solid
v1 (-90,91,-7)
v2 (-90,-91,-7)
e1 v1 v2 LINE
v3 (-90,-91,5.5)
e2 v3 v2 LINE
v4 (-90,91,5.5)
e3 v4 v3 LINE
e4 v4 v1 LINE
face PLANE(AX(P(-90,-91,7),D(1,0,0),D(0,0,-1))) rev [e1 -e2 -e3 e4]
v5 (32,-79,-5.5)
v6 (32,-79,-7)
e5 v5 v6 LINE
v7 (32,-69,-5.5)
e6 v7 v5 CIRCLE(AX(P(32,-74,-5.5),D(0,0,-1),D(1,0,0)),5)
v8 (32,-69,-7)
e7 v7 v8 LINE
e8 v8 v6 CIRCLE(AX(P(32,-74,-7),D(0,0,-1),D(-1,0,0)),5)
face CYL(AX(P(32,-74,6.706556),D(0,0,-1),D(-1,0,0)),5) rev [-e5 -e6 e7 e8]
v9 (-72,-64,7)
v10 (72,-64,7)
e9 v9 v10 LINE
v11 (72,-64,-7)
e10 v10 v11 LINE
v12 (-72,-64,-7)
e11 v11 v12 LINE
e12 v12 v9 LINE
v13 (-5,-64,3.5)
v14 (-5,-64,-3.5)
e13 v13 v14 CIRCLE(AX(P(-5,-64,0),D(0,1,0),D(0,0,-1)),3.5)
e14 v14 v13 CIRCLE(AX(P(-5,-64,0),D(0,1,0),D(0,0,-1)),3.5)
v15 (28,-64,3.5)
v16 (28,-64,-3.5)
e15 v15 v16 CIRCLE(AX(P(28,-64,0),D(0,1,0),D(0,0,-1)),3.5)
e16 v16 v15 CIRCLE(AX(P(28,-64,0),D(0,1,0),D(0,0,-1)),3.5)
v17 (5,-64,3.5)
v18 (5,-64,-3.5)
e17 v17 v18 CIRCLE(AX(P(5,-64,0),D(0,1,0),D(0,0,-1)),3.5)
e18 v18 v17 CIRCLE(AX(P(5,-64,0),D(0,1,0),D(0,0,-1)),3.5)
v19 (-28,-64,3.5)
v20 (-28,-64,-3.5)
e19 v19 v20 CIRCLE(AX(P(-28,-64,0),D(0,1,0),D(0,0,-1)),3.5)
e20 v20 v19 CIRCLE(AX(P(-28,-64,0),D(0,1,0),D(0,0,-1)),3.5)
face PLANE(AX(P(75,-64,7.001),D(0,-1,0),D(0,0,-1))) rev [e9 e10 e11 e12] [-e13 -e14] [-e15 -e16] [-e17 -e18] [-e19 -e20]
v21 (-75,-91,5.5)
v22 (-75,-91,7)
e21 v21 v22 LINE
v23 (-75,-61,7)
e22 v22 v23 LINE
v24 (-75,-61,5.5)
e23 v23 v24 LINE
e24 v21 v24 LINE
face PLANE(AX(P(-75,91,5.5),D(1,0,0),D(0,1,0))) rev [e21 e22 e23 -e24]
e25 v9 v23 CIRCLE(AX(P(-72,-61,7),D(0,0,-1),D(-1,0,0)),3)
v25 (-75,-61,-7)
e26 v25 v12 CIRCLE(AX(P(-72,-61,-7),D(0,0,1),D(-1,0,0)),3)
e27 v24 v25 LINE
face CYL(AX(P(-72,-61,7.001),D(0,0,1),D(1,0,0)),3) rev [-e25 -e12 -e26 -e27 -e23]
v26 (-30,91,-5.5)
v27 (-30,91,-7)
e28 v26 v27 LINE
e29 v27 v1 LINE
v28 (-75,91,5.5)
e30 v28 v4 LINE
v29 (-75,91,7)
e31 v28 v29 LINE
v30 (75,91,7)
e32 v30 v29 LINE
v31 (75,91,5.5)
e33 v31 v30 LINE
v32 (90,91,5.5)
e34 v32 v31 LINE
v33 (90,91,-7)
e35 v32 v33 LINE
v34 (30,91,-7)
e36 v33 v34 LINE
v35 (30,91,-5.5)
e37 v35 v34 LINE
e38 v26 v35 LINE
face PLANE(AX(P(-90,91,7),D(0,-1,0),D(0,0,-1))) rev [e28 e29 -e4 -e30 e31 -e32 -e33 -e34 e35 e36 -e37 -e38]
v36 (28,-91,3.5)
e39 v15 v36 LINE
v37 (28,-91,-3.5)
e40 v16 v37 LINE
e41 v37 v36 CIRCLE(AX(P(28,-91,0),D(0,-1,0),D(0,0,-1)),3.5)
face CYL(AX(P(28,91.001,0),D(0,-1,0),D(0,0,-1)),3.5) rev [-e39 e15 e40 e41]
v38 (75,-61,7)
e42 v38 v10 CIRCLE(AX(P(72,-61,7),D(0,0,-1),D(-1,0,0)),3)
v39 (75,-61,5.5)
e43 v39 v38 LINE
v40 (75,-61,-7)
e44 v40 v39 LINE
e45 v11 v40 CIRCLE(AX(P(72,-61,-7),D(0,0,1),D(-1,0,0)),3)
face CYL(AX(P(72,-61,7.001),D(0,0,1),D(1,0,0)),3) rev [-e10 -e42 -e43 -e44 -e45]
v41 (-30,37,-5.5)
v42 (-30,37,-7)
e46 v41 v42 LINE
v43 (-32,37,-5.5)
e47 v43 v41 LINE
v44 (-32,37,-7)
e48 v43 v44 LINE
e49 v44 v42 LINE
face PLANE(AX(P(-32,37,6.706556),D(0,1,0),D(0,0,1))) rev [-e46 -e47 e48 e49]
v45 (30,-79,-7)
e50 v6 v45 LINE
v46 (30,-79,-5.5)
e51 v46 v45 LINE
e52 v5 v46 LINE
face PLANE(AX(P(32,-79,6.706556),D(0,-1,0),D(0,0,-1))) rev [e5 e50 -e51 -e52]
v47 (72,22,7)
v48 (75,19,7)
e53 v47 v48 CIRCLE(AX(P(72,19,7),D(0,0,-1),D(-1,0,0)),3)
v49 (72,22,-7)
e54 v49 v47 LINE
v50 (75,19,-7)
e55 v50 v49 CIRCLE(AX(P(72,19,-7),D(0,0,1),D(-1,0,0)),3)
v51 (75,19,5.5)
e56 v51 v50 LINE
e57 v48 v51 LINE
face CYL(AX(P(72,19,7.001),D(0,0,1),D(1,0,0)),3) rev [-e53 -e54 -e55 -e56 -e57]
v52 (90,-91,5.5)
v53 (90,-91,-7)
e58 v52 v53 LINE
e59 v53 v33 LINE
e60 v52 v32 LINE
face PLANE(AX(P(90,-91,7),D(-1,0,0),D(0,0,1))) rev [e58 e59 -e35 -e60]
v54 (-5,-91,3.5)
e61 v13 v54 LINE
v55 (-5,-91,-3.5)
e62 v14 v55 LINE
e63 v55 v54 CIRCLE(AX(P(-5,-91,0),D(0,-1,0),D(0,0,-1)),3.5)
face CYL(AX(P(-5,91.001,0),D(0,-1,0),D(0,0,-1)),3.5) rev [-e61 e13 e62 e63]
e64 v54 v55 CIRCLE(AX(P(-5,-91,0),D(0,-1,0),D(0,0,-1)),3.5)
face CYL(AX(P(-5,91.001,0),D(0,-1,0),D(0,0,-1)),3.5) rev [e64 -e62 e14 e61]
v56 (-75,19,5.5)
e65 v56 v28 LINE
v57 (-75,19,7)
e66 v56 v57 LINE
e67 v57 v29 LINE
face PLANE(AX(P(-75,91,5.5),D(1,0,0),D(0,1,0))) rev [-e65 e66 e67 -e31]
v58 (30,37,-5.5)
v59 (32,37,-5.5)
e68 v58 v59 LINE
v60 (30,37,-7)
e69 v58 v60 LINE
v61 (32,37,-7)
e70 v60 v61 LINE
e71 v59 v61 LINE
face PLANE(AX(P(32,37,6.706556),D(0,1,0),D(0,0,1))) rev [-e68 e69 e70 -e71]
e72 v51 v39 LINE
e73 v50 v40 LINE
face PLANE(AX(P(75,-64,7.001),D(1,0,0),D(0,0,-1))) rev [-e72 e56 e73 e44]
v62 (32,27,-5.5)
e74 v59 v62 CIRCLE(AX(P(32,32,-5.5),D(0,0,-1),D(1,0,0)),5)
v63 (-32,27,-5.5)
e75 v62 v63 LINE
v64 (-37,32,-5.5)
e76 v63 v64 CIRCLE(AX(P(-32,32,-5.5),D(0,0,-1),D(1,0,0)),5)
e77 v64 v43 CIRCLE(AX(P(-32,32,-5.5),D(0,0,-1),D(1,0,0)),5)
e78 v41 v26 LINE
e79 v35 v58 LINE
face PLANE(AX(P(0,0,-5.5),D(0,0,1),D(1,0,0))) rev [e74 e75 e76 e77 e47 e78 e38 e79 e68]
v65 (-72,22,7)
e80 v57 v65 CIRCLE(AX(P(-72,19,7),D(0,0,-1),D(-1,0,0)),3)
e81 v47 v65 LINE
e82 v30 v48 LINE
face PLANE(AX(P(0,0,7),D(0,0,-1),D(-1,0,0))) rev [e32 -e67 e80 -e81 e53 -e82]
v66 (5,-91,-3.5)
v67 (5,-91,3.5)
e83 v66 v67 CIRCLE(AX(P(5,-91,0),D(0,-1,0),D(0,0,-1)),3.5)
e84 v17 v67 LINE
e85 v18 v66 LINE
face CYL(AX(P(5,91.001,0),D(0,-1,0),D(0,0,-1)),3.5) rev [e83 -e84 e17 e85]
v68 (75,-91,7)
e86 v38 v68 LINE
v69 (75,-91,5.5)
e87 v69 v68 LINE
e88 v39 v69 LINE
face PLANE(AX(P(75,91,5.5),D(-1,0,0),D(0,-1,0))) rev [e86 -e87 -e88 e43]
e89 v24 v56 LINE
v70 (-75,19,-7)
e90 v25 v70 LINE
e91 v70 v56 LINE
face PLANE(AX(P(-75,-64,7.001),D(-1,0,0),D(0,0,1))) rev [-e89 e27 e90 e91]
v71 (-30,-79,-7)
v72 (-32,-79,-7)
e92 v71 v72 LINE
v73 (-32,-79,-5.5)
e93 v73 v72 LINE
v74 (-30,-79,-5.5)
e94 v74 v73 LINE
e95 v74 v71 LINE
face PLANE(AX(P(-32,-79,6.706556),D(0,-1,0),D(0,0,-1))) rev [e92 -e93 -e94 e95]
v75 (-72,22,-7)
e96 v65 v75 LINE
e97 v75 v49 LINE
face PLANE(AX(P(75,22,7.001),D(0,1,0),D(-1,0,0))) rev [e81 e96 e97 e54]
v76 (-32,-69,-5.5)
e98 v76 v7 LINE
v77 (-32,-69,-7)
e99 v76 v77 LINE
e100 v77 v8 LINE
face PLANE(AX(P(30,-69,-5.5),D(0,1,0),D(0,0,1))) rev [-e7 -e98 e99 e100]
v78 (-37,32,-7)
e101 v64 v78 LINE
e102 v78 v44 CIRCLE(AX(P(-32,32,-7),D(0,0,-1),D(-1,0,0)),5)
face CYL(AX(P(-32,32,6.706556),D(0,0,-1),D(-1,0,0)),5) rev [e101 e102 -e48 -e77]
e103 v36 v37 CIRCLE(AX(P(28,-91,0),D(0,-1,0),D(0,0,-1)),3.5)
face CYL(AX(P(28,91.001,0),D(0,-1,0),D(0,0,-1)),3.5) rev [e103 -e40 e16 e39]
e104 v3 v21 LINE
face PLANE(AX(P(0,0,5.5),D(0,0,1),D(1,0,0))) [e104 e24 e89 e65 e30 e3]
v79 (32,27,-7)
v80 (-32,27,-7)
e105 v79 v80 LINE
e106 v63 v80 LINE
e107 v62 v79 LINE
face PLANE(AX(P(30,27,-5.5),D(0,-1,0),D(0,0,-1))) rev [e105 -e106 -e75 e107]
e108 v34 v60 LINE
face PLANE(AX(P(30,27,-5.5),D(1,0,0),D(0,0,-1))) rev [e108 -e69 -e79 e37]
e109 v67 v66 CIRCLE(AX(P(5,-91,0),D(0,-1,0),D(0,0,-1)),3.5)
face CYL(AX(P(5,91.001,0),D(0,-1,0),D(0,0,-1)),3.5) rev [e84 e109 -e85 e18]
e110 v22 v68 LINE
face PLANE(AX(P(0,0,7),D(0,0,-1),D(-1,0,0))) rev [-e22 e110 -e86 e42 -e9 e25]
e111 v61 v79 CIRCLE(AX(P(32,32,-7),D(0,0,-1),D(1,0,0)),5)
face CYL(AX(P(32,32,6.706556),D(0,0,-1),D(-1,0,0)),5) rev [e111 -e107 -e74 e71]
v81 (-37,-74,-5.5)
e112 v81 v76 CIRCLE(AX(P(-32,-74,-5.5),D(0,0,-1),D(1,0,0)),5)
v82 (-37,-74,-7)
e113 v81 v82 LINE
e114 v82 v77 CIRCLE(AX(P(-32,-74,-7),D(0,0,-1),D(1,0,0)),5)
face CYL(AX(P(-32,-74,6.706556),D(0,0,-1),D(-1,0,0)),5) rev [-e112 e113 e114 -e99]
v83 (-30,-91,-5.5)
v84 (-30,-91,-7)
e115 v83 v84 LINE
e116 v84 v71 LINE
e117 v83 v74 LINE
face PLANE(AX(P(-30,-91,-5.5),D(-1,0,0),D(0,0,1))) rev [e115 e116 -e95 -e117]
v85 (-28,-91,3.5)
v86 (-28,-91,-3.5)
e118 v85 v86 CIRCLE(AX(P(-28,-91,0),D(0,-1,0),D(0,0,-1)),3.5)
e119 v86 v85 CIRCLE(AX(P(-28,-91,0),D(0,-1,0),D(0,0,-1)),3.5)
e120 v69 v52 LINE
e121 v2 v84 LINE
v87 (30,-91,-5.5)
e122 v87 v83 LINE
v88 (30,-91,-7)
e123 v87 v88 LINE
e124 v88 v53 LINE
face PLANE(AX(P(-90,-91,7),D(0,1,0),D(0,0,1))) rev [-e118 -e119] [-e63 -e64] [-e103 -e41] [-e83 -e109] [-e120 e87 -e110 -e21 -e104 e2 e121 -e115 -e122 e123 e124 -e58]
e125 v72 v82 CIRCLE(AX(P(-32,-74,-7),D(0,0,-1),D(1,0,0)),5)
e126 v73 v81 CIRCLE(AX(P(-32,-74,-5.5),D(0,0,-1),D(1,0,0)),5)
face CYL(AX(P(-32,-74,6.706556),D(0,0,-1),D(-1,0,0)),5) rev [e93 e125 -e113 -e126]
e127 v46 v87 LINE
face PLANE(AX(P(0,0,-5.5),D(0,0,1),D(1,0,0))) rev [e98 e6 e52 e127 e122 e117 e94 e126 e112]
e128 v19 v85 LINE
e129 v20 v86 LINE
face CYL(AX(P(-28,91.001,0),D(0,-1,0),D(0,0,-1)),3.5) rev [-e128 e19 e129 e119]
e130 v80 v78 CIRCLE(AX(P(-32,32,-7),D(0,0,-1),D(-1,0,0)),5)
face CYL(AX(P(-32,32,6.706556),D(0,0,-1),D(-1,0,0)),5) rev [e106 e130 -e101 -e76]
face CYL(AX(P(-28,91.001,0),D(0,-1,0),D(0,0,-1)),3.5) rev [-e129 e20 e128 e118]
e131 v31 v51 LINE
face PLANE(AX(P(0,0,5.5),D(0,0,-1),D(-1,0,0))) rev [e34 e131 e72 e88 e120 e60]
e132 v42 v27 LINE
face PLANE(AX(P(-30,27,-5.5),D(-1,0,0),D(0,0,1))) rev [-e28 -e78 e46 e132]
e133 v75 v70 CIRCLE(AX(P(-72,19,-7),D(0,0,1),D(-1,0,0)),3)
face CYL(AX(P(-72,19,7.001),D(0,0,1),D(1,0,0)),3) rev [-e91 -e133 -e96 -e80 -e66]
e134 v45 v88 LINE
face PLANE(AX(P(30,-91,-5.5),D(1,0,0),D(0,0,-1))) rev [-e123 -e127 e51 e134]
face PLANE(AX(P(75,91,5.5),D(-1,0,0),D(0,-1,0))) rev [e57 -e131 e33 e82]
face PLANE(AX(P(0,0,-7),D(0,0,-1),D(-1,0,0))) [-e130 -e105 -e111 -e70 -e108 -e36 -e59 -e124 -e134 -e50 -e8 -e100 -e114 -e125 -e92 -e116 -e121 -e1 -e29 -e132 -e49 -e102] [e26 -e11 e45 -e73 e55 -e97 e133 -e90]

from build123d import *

# Parameters (mm, degrees)
SKETCH_1_W          = 180
SKETCH_1_H          = 182
EXTRUDE_1_DEPTH     = 7
SKETCH_2_W          = 60
SKETCH_2_H          = 64
SKETCH_2_H_2        = 22
CUT_EXTRUDE_1_DEPTH = 1.5
CUT_EXTRUDE_2_DEPTH = 1.5
CUT_EXTRUDE_3_REACH = 130.752
SKETCH_4_W          = 150
SKETCH_4_H          = 86
FILLET_1_R          = 3
CUT_EXTRUDE_4_REACH = 205.158
SKETCH_6_R          = 3.5
SKETCH_7_W          = 15
SKETCH_7_H          = 182
CUT_EXTRUDE_5_DEPTH = 1.5


with BuildPart() as part:
    # 草图1 → 凸台-拉伸1 (new, symmetric)
    with BuildSketch(Plane.XY):
        Rectangle(SKETCH_1_W, SKETCH_1_H)
    extrude(amount=EXTRUDE_1_DEPTH, both=True)

    # 草图2 → 切除-拉伸1 (cut)
    with BuildSketch(Plane(origin=(0, 0, -7), x_dir=(-1, 0, 0), z_dir=(0, 0, -1))):
        with Locations((0, 59)):
            Rectangle(SKETCH_2_W, SKETCH_2_H)
        with Locations((0, -80)):
            Rectangle(SKETCH_2_W, SKETCH_2_H_2)
    extrude(amount=-CUT_EXTRUDE_1_DEPTH, mode=Mode.SUBTRACT)

    # 草图3 → 切除-拉伸2 (cut)
    with BuildSketch(Plane(origin=(0, 0, -7), x_dir=(-1, 0, 0), z_dir=(0, 0, -1))):
        with BuildLine():
            Line((30, 27), (32, 27))
            ThreePointArc((32, 27), (37, 32), (32, 37))
            Line((32, 37), (30, 37))
            Line((30, 37), (30, 27))
        make_face()
        with BuildLine():
            Line((-30, 37), (-30, 27))
            Line((-30, 27), (-32, 27))
            ThreePointArc((-32, 27), (-37, 32), (-32, 37))
            Line((-32, 37), (-30, 37))
        make_face()
        with BuildLine():
            Line((30, -69), (32, -69))
            ThreePointArc((32, -69), (37, -74), (32, -79))
            Line((32, -79), (30, -79))
            Line((30, -79), (30, -69))
        make_face()
        with BuildLine():
            Line((-30, -79), (-30, -69))
            Line((-30, -69), (-32, -69))
            ThreePointArc((-32, -69), (-37, -74), (-32, -79))
            Line((-32, -79), (-30, -79))
        make_face()
    extrude(amount=-CUT_EXTRUDE_2_DEPTH, mode=Mode.SUBTRACT)

    # 草图4 → 切除-拉伸3 (cut, up to next)
    with BuildSketch(Plane(origin=(0, 0, -7), x_dir=(-1, 0, 0), z_dir=(0, 0, -1)), mode=Mode.PRIVATE) as cut_extrude_3_sk1:
        with Locations((0, -21)):
            Rectangle(SKETCH_4_W, SKETCH_4_H)
    cut_extrude_3_tool1 = extrude(cut_extrude_3_sk1.sketch, amount=-CUT_EXTRUDE_3_REACH, mode=Mode.PRIVATE) & part.part
    add(cut_extrude_3_tool1.solids().sort_by_distance((0, -21, -7))[0], mode=Mode.SUBTRACT)

    # 圆角1
    fillet_1_edges = [part.edges().sort_by_distance(p)[0] for p in [
        (-75, 22, 0),
        (-75, -64, 0),
        (75, -64, 0),
        (75, 22, 0),
    ]]
    fillet(fillet_1_edges, radius=FILLET_1_R)

    # 草图6 → 切除-拉伸4 (cut, up to next)
    with BuildSketch(Plane.XZ.offset(91), mode=Mode.PRIVATE) as cut_extrude_4_sk1:
        with Locations(Location((-28, 0, 0), (0, 0, 270))):
            Circle(SKETCH_6_R)
    cut_extrude_4_tool1 = extrude(cut_extrude_4_sk1.sketch, amount=-CUT_EXTRUDE_4_REACH, mode=Mode.PRIVATE) & part.part
    # 草图6 → 切除-拉伸4 (cut, up to next)
    with BuildSketch(Plane.XZ.offset(91), mode=Mode.PRIVATE) as cut_extrude_4_sk2:
        with Locations(Location((28, 0, 0), (0, 0, 270))):
            Circle(SKETCH_6_R)
    cut_extrude_4_tool2 = extrude(cut_extrude_4_sk2.sketch, amount=-CUT_EXTRUDE_4_REACH, mode=Mode.PRIVATE) & part.part
    # 草图6 → 切除-拉伸4 (cut, up to next)
    with BuildSketch(Plane.XZ.offset(91), mode=Mode.PRIVATE) as cut_extrude_4_sk3:
        with Locations(Location((-5, 0, 0), (0, 0, 270))):
            Circle(SKETCH_6_R)
    cut_extrude_4_tool3 = extrude(cut_extrude_4_sk3.sketch, amount=-CUT_EXTRUDE_4_REACH, mode=Mode.PRIVATE) & part.part
    # 草图6 → 切除-拉伸4 (cut, up to next)
    with BuildSketch(Plane.XZ.offset(91), mode=Mode.PRIVATE) as cut_extrude_4_sk4:
        with Locations(Location((5, 0, 0), (0, 0, 270))):
            Circle(SKETCH_6_R)
    cut_extrude_4_tool4 = extrude(cut_extrude_4_sk4.sketch, amount=-CUT_EXTRUDE_4_REACH, mode=Mode.PRIVATE) & part.part
    add(cut_extrude_4_tool1.solids().sort_by_distance((-28, -91, 0))[0], mode=Mode.SUBTRACT)
    add(cut_extrude_4_tool2.solids().sort_by_distance((28, -91, 0))[0], mode=Mode.SUBTRACT)
    add(cut_extrude_4_tool3.solids().sort_by_distance((-5, -91, 0))[0], mode=Mode.SUBTRACT)
    add(cut_extrude_4_tool4.solids().sort_by_distance((5, -91, 0))[0], mode=Mode.SUBTRACT)

    # 草图7 → 切除-拉伸5 (cut)
    with BuildSketch(Plane.XY.offset(7)):
        with Locations((-82.5, 0)):
            Rectangle(SKETCH_7_W, SKETCH_7_H)
        with Locations((82.5, 0)):
            Rectangle(SKETCH_7_W, SKETCH_7_H)
    extrude(amount=-CUT_EXTRUDE_5_DEPTH, mode=Mode.SUBTRACT)


solid = part.part
